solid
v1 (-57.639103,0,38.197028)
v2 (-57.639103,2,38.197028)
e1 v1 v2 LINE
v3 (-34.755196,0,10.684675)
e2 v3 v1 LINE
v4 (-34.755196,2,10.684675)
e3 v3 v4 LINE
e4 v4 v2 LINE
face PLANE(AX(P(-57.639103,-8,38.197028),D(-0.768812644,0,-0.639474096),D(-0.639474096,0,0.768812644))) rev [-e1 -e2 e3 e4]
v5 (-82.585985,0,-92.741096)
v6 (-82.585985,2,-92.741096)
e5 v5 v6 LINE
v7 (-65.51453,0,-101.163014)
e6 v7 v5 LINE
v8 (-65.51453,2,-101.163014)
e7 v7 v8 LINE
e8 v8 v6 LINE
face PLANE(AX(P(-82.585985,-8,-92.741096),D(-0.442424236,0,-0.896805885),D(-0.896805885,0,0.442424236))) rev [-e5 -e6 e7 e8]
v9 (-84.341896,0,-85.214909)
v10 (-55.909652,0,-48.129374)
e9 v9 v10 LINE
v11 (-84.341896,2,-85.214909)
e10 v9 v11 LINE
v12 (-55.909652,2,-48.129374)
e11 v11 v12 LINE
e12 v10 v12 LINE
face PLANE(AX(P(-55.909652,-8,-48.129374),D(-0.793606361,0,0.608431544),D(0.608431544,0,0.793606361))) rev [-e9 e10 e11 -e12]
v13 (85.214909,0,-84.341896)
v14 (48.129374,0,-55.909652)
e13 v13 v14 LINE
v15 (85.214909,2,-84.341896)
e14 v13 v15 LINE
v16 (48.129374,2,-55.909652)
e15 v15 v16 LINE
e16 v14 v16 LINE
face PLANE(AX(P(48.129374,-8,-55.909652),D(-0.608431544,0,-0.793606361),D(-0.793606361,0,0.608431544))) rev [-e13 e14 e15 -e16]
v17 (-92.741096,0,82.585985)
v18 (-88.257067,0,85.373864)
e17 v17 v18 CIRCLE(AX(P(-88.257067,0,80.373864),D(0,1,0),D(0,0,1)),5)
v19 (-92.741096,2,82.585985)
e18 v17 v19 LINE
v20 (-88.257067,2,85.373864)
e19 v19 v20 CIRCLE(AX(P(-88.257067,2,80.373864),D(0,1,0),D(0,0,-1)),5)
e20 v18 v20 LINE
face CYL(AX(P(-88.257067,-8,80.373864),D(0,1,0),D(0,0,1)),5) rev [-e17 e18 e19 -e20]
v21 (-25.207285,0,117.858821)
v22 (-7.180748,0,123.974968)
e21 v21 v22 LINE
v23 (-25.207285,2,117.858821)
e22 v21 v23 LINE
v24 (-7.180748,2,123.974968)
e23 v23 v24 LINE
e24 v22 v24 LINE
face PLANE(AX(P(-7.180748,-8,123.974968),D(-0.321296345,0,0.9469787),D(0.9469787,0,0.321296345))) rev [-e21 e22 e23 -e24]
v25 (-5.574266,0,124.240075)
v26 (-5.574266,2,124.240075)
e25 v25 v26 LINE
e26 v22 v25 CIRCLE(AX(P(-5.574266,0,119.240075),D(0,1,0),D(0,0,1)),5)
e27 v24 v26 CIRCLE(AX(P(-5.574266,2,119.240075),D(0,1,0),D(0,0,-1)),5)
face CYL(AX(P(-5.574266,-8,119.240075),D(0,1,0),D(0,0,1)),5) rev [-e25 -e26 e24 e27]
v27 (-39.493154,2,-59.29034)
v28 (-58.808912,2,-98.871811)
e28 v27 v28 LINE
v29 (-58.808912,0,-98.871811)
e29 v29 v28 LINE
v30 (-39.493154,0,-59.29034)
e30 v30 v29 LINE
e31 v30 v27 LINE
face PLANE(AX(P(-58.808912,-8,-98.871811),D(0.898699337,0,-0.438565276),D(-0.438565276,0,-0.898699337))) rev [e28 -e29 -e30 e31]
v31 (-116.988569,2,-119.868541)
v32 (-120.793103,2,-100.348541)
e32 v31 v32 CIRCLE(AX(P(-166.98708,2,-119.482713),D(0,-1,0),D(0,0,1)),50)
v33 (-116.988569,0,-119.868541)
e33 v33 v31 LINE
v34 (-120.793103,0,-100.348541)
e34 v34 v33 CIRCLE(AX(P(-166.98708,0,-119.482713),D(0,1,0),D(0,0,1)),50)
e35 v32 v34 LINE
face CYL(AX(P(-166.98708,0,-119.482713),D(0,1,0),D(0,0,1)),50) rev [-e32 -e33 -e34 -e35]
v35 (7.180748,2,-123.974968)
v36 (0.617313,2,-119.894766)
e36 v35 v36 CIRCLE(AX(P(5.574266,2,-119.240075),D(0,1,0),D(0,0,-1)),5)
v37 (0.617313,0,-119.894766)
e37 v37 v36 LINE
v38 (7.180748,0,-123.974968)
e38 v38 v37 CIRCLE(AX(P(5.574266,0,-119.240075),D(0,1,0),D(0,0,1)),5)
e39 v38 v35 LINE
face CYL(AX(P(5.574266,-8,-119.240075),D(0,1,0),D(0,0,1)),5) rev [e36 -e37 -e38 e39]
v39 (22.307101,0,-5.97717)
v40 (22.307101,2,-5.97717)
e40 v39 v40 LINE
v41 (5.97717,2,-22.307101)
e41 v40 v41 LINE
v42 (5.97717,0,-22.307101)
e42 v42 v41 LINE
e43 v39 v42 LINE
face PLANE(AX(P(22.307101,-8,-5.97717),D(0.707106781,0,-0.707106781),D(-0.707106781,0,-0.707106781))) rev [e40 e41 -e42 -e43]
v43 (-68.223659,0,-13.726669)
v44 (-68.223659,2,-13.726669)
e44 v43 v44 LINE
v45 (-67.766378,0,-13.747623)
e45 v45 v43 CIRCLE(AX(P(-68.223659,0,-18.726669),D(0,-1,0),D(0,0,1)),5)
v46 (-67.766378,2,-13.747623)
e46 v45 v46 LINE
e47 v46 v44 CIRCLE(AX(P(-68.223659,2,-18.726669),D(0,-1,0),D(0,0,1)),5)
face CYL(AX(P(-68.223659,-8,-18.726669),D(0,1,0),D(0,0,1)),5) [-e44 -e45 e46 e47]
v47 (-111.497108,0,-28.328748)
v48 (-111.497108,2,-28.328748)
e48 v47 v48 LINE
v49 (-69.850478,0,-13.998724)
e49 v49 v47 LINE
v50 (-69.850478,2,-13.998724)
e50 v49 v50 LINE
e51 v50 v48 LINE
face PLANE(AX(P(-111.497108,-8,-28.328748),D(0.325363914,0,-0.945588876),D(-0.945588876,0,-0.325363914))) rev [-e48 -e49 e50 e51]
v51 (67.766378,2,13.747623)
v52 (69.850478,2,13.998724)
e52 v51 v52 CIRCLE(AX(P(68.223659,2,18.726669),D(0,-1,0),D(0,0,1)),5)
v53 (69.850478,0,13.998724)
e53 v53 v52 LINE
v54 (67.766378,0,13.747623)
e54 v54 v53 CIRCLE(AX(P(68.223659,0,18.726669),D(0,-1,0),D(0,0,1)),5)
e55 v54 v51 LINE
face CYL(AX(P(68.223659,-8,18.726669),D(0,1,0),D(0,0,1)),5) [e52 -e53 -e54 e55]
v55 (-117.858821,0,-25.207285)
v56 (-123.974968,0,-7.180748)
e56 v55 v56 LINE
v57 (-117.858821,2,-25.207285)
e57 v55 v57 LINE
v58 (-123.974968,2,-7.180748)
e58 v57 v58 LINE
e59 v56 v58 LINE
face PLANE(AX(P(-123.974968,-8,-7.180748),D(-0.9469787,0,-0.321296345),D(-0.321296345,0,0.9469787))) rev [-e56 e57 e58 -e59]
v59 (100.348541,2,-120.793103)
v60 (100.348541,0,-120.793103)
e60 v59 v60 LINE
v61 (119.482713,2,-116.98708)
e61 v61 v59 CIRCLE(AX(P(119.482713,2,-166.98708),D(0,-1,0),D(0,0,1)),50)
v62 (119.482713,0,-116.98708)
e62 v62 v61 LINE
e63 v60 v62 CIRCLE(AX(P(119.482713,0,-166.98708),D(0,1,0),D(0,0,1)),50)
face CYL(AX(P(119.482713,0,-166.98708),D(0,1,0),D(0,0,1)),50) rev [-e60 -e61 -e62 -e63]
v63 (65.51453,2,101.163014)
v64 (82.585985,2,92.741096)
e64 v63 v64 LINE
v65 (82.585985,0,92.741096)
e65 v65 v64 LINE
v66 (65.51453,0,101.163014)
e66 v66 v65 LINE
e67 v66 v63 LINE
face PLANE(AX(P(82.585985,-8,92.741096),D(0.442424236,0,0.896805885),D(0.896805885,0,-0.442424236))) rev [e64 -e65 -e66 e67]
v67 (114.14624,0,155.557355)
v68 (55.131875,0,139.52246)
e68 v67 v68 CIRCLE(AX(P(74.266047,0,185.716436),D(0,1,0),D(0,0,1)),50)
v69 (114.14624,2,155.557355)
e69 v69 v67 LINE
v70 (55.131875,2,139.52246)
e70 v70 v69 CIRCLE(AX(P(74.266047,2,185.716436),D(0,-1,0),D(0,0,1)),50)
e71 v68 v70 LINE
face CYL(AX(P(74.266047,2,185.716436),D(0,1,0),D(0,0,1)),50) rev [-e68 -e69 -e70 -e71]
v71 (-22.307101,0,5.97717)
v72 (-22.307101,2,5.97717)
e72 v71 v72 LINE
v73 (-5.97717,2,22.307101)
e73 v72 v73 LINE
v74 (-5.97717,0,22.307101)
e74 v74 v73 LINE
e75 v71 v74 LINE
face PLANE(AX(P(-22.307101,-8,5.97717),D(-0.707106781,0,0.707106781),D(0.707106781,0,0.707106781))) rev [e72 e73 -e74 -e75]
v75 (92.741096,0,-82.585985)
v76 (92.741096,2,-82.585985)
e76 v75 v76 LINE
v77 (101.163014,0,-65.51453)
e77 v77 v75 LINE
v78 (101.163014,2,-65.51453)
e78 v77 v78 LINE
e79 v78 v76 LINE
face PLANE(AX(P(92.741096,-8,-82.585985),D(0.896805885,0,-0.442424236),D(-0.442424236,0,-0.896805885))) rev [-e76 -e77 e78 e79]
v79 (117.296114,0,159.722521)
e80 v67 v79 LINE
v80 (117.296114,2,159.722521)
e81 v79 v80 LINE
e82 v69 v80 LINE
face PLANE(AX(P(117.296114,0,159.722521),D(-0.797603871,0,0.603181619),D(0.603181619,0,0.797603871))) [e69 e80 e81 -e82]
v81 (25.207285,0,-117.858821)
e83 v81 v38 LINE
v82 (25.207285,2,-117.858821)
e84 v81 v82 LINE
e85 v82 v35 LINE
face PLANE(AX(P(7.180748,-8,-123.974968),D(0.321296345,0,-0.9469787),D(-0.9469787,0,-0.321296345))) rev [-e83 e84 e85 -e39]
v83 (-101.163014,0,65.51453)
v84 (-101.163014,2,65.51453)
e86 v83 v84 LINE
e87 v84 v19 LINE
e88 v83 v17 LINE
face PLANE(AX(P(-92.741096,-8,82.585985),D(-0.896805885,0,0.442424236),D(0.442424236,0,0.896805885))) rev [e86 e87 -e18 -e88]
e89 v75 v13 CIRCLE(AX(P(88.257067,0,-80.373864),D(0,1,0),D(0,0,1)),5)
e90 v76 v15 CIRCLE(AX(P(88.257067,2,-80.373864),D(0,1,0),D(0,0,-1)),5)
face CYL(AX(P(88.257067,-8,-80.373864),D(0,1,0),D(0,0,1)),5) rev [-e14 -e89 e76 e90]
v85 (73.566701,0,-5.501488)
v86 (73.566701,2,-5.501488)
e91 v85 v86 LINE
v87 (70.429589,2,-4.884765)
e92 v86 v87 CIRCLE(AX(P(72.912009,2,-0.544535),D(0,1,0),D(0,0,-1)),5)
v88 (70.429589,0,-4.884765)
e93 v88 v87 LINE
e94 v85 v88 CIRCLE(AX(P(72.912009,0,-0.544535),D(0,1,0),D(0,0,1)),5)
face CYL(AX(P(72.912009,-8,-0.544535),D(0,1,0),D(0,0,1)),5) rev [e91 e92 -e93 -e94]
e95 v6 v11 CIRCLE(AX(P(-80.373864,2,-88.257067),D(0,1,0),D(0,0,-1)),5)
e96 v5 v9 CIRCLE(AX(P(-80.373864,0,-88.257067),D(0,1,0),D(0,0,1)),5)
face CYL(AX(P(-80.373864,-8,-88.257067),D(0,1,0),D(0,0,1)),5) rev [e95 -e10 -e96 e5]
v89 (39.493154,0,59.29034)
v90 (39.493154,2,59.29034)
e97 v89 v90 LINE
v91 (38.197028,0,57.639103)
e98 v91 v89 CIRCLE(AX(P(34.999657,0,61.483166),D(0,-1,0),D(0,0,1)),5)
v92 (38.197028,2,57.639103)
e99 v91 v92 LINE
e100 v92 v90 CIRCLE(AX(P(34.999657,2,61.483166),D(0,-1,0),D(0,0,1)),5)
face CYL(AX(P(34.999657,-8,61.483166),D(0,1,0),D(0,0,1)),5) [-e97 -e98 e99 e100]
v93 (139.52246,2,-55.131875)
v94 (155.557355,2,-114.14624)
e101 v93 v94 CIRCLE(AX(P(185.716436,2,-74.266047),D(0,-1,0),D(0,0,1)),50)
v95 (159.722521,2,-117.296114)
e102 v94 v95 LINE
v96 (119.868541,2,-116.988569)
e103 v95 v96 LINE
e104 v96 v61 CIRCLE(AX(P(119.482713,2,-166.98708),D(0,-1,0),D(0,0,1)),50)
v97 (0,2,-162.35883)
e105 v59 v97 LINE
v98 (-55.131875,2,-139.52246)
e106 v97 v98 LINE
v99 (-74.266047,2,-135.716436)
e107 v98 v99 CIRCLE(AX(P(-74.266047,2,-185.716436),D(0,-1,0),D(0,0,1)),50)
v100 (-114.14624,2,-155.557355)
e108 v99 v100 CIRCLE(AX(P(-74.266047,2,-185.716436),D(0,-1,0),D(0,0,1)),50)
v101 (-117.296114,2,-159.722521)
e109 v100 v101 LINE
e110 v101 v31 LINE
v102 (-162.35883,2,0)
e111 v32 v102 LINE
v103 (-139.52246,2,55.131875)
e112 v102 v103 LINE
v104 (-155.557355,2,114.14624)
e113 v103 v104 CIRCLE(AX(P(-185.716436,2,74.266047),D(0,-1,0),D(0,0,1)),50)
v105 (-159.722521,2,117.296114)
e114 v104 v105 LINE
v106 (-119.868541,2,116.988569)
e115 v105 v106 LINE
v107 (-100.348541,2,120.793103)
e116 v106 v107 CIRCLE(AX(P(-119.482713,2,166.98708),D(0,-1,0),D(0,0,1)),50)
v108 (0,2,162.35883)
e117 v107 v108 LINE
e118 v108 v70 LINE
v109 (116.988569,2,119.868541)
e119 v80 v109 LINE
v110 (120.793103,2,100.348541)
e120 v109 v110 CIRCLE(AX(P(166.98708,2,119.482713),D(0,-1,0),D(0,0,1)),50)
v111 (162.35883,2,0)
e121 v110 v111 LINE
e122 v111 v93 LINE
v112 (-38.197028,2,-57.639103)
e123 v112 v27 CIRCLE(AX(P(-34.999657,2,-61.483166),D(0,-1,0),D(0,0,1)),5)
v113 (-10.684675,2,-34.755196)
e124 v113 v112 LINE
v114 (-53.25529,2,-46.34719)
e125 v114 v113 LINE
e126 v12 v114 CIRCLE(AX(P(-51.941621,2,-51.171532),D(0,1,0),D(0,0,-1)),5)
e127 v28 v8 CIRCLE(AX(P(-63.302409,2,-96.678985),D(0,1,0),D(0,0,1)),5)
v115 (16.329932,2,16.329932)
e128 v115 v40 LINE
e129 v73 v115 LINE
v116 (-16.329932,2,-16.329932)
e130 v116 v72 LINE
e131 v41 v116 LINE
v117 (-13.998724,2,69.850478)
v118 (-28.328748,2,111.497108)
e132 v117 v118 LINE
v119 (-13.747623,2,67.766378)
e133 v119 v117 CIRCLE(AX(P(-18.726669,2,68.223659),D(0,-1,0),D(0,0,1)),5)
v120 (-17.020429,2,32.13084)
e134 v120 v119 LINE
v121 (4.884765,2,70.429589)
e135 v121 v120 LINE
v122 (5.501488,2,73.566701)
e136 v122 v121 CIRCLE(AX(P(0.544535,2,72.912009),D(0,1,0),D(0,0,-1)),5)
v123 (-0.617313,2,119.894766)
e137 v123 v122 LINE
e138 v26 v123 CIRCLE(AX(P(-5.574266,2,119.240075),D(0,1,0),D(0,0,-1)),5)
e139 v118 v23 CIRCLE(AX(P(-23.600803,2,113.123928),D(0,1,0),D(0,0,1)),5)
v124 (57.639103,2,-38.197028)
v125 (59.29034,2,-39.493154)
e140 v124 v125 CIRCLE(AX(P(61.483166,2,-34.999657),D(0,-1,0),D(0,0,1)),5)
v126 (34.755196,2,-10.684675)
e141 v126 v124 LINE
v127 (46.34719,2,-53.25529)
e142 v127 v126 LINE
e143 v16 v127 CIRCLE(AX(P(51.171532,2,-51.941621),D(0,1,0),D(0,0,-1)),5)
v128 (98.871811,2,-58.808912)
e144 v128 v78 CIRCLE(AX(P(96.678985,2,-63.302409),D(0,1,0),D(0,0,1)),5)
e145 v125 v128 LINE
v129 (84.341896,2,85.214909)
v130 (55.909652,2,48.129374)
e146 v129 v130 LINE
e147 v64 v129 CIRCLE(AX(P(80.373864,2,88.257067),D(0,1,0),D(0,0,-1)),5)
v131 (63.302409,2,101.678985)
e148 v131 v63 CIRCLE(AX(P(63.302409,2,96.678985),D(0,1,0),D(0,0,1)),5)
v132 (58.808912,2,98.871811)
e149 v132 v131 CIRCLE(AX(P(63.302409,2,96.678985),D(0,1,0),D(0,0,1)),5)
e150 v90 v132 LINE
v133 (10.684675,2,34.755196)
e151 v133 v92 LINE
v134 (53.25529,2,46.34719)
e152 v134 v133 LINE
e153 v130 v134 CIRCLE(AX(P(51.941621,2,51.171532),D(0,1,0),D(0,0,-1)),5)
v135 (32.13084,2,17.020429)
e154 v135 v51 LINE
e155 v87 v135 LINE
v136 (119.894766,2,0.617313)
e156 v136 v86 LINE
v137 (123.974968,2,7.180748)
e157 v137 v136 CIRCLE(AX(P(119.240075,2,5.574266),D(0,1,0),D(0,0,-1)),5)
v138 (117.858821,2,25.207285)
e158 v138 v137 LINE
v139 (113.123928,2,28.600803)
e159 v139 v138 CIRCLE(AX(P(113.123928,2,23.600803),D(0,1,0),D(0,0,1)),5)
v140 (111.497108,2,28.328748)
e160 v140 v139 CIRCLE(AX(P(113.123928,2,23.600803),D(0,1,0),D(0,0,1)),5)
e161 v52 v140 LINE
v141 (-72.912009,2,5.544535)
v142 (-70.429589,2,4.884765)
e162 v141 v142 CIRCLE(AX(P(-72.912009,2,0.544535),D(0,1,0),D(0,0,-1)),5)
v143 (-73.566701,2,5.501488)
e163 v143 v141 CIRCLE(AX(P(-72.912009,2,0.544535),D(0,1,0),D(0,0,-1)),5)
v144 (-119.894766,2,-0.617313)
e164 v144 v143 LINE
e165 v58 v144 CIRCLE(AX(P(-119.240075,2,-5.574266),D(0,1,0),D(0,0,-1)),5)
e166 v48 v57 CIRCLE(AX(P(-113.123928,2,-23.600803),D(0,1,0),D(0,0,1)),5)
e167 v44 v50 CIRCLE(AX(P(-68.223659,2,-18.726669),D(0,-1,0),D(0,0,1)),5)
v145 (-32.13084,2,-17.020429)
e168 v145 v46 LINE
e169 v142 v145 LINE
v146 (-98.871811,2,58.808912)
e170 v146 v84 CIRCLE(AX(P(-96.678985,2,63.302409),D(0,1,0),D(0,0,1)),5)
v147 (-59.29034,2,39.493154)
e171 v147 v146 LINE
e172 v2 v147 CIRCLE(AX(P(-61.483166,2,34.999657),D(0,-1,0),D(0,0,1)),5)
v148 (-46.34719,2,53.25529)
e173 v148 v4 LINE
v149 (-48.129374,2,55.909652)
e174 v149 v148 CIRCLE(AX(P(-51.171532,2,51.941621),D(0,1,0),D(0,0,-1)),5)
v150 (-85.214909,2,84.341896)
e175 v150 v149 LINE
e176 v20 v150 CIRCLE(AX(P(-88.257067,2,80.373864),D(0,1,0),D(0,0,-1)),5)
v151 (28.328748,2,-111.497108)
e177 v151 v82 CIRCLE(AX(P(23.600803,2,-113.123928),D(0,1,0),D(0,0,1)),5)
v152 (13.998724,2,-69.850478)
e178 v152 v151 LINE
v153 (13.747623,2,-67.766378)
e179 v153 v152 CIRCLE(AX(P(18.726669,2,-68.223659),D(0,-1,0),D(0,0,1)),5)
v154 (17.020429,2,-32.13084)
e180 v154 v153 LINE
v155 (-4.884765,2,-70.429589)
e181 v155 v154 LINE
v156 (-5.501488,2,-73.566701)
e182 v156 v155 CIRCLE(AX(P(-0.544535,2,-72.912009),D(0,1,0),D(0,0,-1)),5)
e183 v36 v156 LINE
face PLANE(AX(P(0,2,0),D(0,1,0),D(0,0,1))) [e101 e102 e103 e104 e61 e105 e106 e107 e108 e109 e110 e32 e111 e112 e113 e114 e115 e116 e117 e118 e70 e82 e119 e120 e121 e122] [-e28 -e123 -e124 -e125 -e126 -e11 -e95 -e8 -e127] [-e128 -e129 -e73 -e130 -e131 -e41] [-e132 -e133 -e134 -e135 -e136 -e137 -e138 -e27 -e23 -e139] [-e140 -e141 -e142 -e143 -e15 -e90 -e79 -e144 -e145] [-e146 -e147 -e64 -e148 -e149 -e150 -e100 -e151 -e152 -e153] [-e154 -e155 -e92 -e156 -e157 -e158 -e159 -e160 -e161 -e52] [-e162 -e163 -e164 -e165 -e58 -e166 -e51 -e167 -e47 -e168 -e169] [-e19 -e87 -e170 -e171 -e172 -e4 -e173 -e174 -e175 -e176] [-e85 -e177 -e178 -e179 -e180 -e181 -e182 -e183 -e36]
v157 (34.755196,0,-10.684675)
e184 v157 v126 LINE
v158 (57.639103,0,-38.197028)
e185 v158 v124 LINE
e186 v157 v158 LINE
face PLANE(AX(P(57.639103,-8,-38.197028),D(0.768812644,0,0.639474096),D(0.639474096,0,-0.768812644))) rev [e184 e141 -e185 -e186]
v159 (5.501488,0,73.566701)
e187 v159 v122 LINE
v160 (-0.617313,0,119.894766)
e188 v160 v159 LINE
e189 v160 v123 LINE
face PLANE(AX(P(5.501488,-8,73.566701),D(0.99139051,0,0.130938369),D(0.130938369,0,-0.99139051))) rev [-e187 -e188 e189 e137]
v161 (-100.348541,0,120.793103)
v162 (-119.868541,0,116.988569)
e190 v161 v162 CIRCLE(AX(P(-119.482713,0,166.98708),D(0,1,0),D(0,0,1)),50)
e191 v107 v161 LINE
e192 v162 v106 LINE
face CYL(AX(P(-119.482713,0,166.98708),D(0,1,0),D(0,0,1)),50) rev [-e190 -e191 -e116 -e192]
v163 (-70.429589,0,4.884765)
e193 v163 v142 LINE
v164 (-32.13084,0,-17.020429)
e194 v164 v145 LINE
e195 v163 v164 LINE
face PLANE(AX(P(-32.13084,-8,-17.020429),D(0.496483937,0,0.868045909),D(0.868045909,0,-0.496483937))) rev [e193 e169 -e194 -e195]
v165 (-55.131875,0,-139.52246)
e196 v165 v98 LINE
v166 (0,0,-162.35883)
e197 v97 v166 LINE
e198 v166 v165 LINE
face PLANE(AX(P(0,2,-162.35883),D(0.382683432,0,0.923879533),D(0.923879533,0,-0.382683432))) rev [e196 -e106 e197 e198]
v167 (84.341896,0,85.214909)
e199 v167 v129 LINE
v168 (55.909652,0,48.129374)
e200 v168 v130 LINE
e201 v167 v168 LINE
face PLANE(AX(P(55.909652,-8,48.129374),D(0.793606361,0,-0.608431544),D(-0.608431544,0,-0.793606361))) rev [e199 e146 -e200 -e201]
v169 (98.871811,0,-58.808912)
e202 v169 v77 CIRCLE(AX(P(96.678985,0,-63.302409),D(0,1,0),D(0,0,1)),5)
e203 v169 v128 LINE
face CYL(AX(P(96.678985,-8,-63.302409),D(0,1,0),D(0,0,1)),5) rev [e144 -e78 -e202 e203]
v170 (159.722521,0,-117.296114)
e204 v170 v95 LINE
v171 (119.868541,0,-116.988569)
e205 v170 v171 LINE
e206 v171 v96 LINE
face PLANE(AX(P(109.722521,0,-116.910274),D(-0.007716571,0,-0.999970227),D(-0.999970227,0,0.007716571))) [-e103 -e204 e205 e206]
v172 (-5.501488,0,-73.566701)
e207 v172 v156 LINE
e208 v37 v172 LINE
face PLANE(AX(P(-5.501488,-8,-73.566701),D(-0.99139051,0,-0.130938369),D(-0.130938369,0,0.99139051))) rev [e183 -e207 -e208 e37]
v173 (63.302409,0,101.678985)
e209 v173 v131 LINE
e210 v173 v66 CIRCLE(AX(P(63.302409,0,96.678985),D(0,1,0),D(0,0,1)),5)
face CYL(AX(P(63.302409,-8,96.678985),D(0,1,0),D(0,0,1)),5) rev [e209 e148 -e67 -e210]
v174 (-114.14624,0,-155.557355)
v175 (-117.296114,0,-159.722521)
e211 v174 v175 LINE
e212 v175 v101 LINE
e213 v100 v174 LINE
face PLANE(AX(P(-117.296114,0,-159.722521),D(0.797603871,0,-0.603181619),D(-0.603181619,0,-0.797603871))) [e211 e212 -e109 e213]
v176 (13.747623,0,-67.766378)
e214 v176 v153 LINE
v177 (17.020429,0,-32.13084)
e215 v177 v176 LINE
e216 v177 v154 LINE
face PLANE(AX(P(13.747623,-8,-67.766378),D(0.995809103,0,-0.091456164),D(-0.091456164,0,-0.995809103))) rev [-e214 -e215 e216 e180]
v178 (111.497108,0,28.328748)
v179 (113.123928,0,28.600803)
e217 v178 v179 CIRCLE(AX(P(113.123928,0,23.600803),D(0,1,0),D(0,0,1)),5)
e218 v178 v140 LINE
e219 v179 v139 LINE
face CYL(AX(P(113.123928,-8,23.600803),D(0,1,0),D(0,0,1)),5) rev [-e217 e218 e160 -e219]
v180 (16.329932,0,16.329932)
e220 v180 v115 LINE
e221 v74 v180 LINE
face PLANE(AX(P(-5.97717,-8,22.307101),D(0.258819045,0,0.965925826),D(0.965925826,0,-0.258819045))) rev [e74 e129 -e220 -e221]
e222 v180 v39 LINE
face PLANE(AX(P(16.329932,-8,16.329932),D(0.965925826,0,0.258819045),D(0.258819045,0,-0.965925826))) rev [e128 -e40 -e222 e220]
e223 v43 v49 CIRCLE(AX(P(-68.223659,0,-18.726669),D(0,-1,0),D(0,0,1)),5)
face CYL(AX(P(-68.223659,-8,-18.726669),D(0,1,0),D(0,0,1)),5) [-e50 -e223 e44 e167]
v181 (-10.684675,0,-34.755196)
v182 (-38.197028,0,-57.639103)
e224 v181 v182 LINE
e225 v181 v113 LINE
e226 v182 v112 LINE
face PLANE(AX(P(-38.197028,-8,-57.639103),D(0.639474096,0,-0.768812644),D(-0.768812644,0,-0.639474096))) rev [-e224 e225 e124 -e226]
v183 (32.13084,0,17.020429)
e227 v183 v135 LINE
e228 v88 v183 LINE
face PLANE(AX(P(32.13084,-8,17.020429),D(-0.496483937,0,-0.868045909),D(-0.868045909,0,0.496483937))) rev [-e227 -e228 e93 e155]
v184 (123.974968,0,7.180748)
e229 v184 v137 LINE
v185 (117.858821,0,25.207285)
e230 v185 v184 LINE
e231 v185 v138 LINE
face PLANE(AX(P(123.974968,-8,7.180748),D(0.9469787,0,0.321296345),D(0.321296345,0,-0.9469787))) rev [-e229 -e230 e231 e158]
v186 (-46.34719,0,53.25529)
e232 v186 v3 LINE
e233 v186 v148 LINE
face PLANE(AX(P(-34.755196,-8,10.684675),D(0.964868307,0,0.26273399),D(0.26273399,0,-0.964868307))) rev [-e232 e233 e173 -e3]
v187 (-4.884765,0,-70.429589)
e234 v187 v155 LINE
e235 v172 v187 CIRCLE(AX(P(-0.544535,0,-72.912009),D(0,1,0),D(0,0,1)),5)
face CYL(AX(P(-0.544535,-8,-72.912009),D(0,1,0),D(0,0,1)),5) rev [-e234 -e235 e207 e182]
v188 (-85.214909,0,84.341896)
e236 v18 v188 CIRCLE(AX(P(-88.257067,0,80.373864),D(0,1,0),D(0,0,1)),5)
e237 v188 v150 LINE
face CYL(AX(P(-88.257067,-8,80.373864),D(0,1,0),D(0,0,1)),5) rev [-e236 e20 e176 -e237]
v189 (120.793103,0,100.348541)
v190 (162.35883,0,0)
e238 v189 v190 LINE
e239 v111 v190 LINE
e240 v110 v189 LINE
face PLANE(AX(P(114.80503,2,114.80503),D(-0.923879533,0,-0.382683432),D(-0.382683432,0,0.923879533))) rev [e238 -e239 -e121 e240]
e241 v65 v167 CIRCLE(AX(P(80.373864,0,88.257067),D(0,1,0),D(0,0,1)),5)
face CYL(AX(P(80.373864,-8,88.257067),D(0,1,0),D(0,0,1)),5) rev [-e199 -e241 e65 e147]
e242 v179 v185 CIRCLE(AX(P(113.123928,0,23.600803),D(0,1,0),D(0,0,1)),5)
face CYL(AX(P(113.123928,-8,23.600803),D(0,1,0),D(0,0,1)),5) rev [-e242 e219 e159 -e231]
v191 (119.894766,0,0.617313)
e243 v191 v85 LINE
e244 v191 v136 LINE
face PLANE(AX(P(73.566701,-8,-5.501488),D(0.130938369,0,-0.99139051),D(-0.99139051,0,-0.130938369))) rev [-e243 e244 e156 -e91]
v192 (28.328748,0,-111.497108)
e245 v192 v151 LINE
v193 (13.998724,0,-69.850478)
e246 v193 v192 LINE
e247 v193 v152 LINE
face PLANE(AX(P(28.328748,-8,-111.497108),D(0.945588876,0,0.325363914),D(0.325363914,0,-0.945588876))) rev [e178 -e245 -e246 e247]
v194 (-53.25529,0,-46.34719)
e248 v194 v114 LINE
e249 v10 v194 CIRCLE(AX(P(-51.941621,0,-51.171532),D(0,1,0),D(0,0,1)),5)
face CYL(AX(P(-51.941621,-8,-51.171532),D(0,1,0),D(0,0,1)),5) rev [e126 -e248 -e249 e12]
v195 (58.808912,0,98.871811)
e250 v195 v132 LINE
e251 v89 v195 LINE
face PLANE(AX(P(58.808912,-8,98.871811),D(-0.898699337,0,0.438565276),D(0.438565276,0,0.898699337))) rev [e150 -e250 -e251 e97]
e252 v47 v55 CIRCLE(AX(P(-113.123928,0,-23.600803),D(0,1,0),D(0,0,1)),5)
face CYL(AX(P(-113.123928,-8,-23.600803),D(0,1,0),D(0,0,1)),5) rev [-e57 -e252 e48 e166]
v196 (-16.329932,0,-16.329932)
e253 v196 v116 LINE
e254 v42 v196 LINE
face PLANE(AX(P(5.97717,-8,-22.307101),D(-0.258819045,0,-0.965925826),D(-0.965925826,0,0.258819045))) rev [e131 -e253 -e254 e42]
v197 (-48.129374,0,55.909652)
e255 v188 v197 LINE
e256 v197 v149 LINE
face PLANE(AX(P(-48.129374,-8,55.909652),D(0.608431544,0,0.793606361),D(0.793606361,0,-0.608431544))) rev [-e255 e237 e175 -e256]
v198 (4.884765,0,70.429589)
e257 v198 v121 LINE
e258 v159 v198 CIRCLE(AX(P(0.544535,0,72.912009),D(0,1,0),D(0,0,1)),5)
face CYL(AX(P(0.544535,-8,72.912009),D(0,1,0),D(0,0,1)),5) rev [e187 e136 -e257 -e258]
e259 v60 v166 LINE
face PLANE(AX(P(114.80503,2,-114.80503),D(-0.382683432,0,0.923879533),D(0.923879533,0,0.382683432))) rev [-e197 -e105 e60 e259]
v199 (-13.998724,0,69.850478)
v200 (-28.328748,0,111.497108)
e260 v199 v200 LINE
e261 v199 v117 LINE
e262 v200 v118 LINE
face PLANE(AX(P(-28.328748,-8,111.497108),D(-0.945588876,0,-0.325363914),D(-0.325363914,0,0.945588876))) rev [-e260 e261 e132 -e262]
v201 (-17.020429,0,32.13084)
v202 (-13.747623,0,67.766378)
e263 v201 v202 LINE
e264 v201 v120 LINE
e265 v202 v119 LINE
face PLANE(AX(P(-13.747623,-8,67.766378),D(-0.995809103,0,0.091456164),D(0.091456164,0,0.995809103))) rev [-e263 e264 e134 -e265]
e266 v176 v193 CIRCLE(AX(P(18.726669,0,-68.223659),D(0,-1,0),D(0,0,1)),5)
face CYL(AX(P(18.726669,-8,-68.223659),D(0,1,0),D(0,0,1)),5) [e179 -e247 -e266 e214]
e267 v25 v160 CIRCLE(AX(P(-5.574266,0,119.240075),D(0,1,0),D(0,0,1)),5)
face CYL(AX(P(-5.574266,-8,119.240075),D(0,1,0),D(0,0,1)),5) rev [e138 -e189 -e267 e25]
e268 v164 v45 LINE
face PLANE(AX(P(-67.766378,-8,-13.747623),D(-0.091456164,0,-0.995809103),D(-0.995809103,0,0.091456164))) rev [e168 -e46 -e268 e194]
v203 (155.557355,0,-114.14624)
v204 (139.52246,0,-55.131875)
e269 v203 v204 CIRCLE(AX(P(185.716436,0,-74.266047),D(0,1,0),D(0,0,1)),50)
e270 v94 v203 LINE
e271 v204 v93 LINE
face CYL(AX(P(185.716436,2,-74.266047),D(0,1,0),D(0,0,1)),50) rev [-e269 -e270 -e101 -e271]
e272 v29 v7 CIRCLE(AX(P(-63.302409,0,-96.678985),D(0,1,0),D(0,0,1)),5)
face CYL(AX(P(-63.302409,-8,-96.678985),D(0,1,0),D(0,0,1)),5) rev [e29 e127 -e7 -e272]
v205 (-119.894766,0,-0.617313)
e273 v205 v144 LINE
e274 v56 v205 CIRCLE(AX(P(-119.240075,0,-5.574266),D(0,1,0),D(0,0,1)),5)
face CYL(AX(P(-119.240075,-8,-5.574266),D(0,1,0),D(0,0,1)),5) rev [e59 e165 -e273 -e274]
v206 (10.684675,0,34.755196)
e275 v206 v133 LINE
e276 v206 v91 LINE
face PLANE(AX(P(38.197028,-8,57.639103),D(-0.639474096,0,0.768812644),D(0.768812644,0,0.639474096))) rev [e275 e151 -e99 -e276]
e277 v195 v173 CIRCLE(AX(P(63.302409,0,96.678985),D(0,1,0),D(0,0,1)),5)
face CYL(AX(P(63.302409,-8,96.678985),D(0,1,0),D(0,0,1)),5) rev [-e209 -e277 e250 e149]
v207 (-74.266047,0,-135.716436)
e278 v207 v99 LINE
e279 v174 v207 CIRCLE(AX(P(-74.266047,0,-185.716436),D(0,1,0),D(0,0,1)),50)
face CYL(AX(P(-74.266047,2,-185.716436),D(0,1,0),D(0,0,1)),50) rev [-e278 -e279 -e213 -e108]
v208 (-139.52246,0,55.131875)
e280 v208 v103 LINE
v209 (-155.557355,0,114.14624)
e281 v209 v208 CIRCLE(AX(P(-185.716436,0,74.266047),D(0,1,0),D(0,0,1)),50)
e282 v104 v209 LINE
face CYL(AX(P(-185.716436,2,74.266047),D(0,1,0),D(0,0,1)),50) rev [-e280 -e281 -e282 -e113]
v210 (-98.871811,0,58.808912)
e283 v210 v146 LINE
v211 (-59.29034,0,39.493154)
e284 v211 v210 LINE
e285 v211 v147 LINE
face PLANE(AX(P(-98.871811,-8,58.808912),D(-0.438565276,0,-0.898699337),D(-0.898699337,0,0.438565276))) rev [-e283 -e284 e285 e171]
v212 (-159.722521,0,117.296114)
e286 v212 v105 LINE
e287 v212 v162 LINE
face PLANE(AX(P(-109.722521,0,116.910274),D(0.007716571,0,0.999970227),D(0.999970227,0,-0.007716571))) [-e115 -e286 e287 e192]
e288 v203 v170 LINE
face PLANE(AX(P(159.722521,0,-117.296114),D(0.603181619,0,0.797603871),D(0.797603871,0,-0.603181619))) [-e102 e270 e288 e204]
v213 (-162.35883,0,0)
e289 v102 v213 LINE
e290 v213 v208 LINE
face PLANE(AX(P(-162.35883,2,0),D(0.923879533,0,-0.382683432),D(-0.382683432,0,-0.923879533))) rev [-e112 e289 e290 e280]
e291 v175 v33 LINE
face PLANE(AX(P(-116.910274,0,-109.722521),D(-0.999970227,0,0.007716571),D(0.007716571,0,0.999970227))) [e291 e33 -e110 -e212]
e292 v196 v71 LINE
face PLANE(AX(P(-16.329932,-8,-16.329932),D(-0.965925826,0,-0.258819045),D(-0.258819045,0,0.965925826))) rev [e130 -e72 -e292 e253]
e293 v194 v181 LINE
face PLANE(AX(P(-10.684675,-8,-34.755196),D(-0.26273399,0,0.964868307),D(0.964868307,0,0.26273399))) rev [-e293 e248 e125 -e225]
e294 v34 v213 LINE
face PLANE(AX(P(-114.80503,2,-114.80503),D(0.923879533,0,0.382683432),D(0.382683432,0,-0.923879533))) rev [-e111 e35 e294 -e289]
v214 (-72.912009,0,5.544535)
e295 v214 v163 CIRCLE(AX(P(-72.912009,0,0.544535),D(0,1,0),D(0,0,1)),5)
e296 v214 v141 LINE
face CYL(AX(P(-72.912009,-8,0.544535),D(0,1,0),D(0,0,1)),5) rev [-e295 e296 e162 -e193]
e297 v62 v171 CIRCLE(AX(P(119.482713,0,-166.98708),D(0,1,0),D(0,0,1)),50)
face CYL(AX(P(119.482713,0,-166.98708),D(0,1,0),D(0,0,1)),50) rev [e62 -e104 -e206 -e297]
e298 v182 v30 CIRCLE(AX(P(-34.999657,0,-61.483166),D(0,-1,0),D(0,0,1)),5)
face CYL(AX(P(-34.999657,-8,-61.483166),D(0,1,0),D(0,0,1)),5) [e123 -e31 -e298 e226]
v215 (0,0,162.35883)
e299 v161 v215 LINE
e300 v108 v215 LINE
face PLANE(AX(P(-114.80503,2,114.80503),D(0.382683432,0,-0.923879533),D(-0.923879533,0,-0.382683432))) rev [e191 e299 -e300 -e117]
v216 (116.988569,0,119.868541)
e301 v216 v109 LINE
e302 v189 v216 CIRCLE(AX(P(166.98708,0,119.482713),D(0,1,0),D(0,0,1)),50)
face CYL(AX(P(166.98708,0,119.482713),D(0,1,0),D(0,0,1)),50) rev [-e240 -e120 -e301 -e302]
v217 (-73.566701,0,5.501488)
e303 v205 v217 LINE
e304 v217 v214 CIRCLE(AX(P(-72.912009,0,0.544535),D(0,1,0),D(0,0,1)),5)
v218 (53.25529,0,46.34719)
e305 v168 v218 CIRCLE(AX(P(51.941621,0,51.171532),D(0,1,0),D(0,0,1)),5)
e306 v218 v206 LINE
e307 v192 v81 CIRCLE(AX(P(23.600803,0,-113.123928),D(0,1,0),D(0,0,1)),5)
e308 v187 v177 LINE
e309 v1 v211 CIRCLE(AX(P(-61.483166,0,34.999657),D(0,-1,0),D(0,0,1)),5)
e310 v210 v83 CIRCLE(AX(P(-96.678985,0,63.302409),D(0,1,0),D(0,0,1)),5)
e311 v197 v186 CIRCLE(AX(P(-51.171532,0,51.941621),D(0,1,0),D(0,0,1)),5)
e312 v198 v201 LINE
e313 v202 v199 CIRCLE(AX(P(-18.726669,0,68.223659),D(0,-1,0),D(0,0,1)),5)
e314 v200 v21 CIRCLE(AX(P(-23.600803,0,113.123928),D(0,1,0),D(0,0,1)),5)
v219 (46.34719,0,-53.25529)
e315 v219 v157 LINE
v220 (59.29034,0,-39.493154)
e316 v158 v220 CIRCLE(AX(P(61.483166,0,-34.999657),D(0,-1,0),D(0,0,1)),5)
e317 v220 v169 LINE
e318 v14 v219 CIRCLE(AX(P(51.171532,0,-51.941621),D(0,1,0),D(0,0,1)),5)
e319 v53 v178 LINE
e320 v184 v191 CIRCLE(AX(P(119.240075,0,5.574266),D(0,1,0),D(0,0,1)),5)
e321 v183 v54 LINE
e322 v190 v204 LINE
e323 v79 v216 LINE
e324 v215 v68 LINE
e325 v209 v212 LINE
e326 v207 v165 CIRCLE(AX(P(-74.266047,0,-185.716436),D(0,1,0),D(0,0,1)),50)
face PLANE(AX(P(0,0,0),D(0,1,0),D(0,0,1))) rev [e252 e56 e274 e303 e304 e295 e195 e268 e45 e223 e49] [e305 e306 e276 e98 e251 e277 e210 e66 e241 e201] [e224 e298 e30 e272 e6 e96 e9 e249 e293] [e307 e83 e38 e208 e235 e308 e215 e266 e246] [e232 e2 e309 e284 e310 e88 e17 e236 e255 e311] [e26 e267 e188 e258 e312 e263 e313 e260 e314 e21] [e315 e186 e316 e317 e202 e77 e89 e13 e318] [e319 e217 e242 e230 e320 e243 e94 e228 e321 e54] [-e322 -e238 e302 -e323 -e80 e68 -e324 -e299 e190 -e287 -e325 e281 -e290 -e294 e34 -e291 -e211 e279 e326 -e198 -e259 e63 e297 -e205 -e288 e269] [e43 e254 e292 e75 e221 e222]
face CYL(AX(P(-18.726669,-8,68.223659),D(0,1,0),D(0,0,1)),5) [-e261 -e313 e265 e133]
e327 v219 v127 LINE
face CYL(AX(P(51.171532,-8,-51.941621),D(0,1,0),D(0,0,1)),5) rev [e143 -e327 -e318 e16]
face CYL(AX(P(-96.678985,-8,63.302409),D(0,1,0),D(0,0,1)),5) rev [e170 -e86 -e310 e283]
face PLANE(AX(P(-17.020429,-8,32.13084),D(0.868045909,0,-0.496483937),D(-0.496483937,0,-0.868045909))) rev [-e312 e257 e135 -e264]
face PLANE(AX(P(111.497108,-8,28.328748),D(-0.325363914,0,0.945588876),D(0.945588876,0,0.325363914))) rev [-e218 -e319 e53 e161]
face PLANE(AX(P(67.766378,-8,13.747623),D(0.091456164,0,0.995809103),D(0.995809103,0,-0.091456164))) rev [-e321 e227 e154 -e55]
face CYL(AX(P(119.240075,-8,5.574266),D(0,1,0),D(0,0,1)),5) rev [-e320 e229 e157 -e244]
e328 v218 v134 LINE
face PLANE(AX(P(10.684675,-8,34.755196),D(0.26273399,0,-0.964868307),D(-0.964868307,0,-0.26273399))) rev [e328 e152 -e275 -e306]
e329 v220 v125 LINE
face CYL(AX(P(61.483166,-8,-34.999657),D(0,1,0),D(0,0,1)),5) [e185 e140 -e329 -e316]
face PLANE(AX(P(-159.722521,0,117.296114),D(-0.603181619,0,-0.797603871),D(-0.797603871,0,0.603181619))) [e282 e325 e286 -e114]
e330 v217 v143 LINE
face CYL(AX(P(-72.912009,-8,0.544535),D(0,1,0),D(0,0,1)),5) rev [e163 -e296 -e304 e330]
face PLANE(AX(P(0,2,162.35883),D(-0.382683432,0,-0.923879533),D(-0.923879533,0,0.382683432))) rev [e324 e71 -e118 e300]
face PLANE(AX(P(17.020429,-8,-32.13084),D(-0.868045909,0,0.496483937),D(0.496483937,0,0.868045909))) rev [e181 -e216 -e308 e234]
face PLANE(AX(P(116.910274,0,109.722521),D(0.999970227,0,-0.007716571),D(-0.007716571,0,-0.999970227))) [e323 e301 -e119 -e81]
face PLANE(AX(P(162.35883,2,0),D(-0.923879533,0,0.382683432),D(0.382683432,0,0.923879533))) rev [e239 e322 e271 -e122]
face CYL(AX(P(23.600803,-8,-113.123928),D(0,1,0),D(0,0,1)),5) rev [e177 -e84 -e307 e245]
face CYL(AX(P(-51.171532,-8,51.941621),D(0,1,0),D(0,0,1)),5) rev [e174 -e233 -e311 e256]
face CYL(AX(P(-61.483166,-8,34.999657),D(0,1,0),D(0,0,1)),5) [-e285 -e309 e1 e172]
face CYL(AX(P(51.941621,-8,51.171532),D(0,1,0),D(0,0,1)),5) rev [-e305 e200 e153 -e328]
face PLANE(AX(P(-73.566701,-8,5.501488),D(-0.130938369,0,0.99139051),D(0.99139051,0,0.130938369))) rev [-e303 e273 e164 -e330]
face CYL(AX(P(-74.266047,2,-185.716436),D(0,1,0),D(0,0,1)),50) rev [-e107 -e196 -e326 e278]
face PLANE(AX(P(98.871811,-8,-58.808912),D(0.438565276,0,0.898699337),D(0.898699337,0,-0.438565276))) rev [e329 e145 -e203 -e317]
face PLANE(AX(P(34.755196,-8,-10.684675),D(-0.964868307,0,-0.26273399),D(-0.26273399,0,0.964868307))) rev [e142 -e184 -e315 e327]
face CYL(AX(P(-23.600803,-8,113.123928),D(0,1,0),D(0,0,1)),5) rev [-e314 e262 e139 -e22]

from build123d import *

# Parameters (mm, degrees)
BOSS_EXTRUDE1_DEPTH = 2
CUT_EXTRUDE1_DEPTH  = 10
CUT_EXTRUDE2_DEPTH  = 10
BOSS_EXTRUDE2_DEPTH = 2
FILLET1_R           = 50


with BuildPart() as part:
    # Sketch1 → Boss-Extrude1 (new body)
    with BuildSketch(Plane(origin=(0, 0, 0), x_dir=(1, 0, 0), z_dir=(0, 1, 0))):
        Polygon((114.80502971, -114.80502971), (162.358830044, 0), (114.80502971, 114.80502971), (0, 162.358830044), (-114.80502971, 114.80502971), (-162.358830044, 0), (-114.80502971, -114.80502971), (0, -162.358830044), align=None)
    extrude(amount=BOSS_EXTRUDE1_DEPTH)

    # Sketch2 → Cut-Extrude1 (cut)
    with BuildSketch(Plane(origin=(0, 2, 0), x_dir=(1, 0, 0), z_dir=(0, 1, 0))):
        Polygon((22.307101433, 5.977169814), (5.977169814, 22.307101433), (-16.329931619, 16.329931619), (-22.307101433, -5.977169814), (-5.977169814, -22.307101433), (16.329931619, -16.329931619), align=None)
    extrude(amount=-CUT_EXTRUDE1_DEPTH, mode=Mode.SUBTRACT)

    # Sketch3 → Cut-Extrude2 (cut)
    with BuildSketch(Plane(origin=(0, 2, 0), x_dir=(1, 0, 0), z_dir=(0, 1, 0))):
        with BuildLine():
            Line((7.180747689, 123.974968015), (25.207285, 117.858821427))
            ThreePointArc((25.207285, 117.858821427), (28.089576698, 115.326406795), (28.328747659, 111.497108353))
            Line((28.328747659, 111.497108353), (13.99872444, 69.850478373))
            ThreePointArc((13.99872444, 69.850478373), (13.762569524, 68.82175425), (13.747623306, 67.766377979))
            Line((13.747623306, 67.766377979), (17.02042887, 32.130840461))
            Line((17.02042887, 32.130840461), (-4.884764675, 70.429589412))
            ThreePointArc((-4.884764675, 70.429589412), (-5.450629901, 71.947522663), (-5.501487679, 73.566700941))
            Line((-5.501487679, 73.566700941), (0.617313414, 119.89476636))
            ThreePointArc((0.617313414, 119.89476636), (2.934488498, 123.486434711), (7.180747689, 123.974968015))
        make_face()
        with BuildLine():
            Line((92.741095966, 82.585985196), (101.163014013, 65.514529695))
            ThreePointArc((101.163014013, 65.514529695), (101.410414459, 61.68575413), (98.871810971, 58.808911827))
            Line((98.871810971, 58.808911827), (59.290339906, 39.493153947))
            ThreePointArc((59.290339906, 39.493153947), (58.395935361, 38.932722886), (57.63910307, 38.197027741))
            Line((57.63910307, 38.197027741), (34.755195848, 10.684674503))
            Line((34.755195848, 10.684674503), (46.347190043, 53.255290495))
            ThreePointArc((46.347190043, 53.255290495), (47.0204038, 54.72875853), (48.129373861, 55.909652349))
            Line((48.129373861, 55.909652349), (85.214908823, 84.34189582))
            ThreePointArc((85.214908823, 84.34189582), (89.393092084, 85.243098653), (92.741095966, 82.585985196))
        make_face()
        with BuildLine():
            Line((123.974968015, -7.180747689), (117.858821427, -25.207285))
            ThreePointArc((117.858821427, -25.207285), (115.326406795, -28.089576698), (111.497108353, -28.328747659))
            Line((111.497108353, -28.328747659), (69.850478373, -13.99872444))
            ThreePointArc((69.850478373, -13.99872444), (68.82175425, -13.762569524), (67.766377979, -13.747623306))
            Line((67.766377979, -13.747623306), (32.130840461, -17.02042887))
            Line((32.130840461, -17.02042887), (70.429589412, 4.884764675))
            ThreePointArc((70.429589412, 4.884764675), (71.947522663, 5.450629901), (73.566700941, 5.501487679))
            Line((73.566700941, 5.501487679), (119.89476636, -0.617313414))
            ThreePointArc((119.89476636, -0.617313414), (123.486434711, -2.934488498), (123.974968015, -7.180747689))
        make_face()
        with BuildLine():
            Line((82.585985196, -92.741095966), (65.514529695, -101.163014013))
            ThreePointArc((65.514529695, -101.163014013), (61.68575413, -101.410414459), (58.808911827, -98.871810971))
            Line((58.808911827, -98.871810971), (39.493153947, -59.290339906))
            ThreePointArc((39.493153947, -59.290339906), (38.932722886, -58.395935361), (38.197027741, -57.63910307))
            Line((38.197027741, -57.63910307), (10.684674503, -34.755195848))
            Line((10.684674503, -34.755195848), (53.255290495, -46.347190043))
            ThreePointArc((53.255290495, -46.347190043), (54.72875853, -47.0204038), (55.909652349, -48.129373861))
            Line((55.909652349, -48.129373861), (84.34189582, -85.214908823))
            ThreePointArc((84.34189582, -85.214908823), (85.243098653, -89.393092084), (82.585985196, -92.741095966))
        make_face()
        with BuildLine():
            Line((-7.180747689, -123.974968015), (-25.207285, -117.858821427))
            ThreePointArc((-25.207285, -117.858821427), (-28.089576698, -115.326406795), (-28.328747659, -111.497108353))
            Line((-28.328747659, -111.497108353), (-13.99872444, -69.850478373))
            ThreePointArc((-13.99872444, -69.850478373), (-13.762569524, -68.82175425), (-13.747623306, -67.766377979))
            Line((-13.747623306, -67.766377979), (-17.02042887, -32.130840461))
            Line((-17.02042887, -32.130840461), (4.884764675, -70.429589412))
            ThreePointArc((4.884764675, -70.429589412), (5.450629901, -71.947522663), (5.501487679, -73.566700941))
            Line((5.501487679, -73.566700941), (-0.617313414, -119.89476636))
            ThreePointArc((-0.617313414, -119.89476636), (-2.934488497, -123.486434711), (-7.180747689, -123.974968015))
        make_face()
        with BuildLine():
            Line((-92.741095966, -82.585985196), (-101.163014013, -65.514529695))
            ThreePointArc((-101.163014013, -65.514529695), (-101.410414459, -61.68575413), (-98.871810971, -58.808911827))
            Line((-98.871810971, -58.808911827), (-59.290339906, -39.493153947))
            ThreePointArc((-59.290339906, -39.493153947), (-58.395935361, -38.932722886), (-57.63910307, -38.197027741))
            Line((-57.63910307, -38.197027741), (-34.755195848, -10.684674503))
            Line((-34.755195848, -10.684674503), (-46.347190043, -53.255290495))
            ThreePointArc((-46.347190043, -53.255290495), (-47.0204038, -54.72875853), (-48.129373861, -55.909652349))
            Line((-48.129373861, -55.909652349), (-85.214908823, -84.34189582))
            ThreePointArc((-85.214908823, -84.34189582), (-89.393092084, -85.243098653), (-92.741095966, -82.585985196))
        make_face()
        with BuildLine():
            Line((-123.974968015, 7.180747689), (-117.858821427, 25.207285))
            ThreePointArc((-117.858821427, 25.207285), (-115.326406795, 28.089576698), (-111.497108353, 28.328747659))
            Line((-111.497108353, 28.328747659), (-69.850478373, 13.99872444))
            ThreePointArc((-69.850478373, 13.99872444), (-68.82175425, 13.762569524), (-67.766377979, 13.747623306))
            Line((-67.766377979, 13.747623306), (-32.130840461, 17.02042887))
            Line((-32.130840461, 17.02042887), (-70.429589412, -4.884764675))
            ThreePointArc((-70.429589412, -4.884764675), (-71.947522663, -5.450629901), (-73.566700941, -5.501487679))
            Line((-73.566700941, -5.501487679), (-119.89476636, 0.617313414))
            ThreePointArc((-119.89476636, 0.617313414), (-123.486434711, 2.934488497), (-123.974968015, 7.180747689))
        make_face()
        with BuildLine():
            Line((-82.585985196, 92.741095966), (-65.514529695, 101.163014013))
            ThreePointArc((-65.514529695, 101.163014013), (-61.68575413, 101.410414459), (-58.808911827, 98.871810971))
            Line((-58.808911827, 98.871810971), (-39.493153947, 59.290339906))
            ThreePointArc((-39.493153947, 59.290339906), (-38.932722886, 58.395935361), (-38.197027741, 57.63910307))
            Line((-38.197027741, 57.63910307), (-10.684674503, 34.755195848))
            Line((-10.684674503, 34.755195848), (-53.255290495, 46.347190043))
            ThreePointArc((-53.255290495, 46.347190043), (-54.72875853, 47.0204038), (-55.909652349, 48.129373861))
            Line((-55.909652349, 48.129373861), (-84.34189582, 85.214908823))
            ThreePointArc((-84.34189582, 85.214908823), (-85.243098653, 89.393092084), (-82.585985196, 92.741095966))
        make_face()
    extrude(amount=-CUT_EXTRUDE2_DEPTH, mode=Mode.SUBTRACT)

    # Sketch6 → Boss-Extrude2 (add)
    with BuildSketch(Plane(origin=(0, 2, 0), x_dir=(1, 0, 0), z_dir=(0, 1, 0))):
        Polygon((-116.910273848, 109.722520758), (-117.296113887, 159.722520758), (-90.835857438, 124.733385943), (-114.80502971, 114.80502971), align=None)
        Polygon((109.722520758, 116.910273848), (159.722520758, 117.296113887), (124.733385943, 90.835857438), (114.80502971, 114.80502971), align=None)
        Polygon((116.910273848, -109.722520758), (117.296113887, -159.722520758), (90.835857438, -124.733385943), (114.80502971, -114.80502971), align=None)
        Polygon((-109.722520758, -116.910273848), (-159.722520758, -117.296113887), (-124.733385943, -90.835857438), (-114.80502971, -114.80502971), align=None)
    extrude(amount=-BOSS_EXTRUDE2_DEPTH)

    # Fillet1
    fillet1_edges = [part.edges().sort_by_distance(p)[0] for p in [
        (-116.910273848, 1, -109.722520758),
        (-90.835857438, 1, -124.733385943),
        (109.722520758, 1, -116.910273848),
        (124.733385943, 1, -90.835857438),
        (116.910273848, 1, 109.722520758),
        (90.835857438, 1, 124.733385943),
        (-109.722520758, 1, 116.910273848),
        (-124.733385943, 1, 90.835857438),
    ]]
    fillet(fillet1_edges, radius=FILLET1_R)


solid = part.part
